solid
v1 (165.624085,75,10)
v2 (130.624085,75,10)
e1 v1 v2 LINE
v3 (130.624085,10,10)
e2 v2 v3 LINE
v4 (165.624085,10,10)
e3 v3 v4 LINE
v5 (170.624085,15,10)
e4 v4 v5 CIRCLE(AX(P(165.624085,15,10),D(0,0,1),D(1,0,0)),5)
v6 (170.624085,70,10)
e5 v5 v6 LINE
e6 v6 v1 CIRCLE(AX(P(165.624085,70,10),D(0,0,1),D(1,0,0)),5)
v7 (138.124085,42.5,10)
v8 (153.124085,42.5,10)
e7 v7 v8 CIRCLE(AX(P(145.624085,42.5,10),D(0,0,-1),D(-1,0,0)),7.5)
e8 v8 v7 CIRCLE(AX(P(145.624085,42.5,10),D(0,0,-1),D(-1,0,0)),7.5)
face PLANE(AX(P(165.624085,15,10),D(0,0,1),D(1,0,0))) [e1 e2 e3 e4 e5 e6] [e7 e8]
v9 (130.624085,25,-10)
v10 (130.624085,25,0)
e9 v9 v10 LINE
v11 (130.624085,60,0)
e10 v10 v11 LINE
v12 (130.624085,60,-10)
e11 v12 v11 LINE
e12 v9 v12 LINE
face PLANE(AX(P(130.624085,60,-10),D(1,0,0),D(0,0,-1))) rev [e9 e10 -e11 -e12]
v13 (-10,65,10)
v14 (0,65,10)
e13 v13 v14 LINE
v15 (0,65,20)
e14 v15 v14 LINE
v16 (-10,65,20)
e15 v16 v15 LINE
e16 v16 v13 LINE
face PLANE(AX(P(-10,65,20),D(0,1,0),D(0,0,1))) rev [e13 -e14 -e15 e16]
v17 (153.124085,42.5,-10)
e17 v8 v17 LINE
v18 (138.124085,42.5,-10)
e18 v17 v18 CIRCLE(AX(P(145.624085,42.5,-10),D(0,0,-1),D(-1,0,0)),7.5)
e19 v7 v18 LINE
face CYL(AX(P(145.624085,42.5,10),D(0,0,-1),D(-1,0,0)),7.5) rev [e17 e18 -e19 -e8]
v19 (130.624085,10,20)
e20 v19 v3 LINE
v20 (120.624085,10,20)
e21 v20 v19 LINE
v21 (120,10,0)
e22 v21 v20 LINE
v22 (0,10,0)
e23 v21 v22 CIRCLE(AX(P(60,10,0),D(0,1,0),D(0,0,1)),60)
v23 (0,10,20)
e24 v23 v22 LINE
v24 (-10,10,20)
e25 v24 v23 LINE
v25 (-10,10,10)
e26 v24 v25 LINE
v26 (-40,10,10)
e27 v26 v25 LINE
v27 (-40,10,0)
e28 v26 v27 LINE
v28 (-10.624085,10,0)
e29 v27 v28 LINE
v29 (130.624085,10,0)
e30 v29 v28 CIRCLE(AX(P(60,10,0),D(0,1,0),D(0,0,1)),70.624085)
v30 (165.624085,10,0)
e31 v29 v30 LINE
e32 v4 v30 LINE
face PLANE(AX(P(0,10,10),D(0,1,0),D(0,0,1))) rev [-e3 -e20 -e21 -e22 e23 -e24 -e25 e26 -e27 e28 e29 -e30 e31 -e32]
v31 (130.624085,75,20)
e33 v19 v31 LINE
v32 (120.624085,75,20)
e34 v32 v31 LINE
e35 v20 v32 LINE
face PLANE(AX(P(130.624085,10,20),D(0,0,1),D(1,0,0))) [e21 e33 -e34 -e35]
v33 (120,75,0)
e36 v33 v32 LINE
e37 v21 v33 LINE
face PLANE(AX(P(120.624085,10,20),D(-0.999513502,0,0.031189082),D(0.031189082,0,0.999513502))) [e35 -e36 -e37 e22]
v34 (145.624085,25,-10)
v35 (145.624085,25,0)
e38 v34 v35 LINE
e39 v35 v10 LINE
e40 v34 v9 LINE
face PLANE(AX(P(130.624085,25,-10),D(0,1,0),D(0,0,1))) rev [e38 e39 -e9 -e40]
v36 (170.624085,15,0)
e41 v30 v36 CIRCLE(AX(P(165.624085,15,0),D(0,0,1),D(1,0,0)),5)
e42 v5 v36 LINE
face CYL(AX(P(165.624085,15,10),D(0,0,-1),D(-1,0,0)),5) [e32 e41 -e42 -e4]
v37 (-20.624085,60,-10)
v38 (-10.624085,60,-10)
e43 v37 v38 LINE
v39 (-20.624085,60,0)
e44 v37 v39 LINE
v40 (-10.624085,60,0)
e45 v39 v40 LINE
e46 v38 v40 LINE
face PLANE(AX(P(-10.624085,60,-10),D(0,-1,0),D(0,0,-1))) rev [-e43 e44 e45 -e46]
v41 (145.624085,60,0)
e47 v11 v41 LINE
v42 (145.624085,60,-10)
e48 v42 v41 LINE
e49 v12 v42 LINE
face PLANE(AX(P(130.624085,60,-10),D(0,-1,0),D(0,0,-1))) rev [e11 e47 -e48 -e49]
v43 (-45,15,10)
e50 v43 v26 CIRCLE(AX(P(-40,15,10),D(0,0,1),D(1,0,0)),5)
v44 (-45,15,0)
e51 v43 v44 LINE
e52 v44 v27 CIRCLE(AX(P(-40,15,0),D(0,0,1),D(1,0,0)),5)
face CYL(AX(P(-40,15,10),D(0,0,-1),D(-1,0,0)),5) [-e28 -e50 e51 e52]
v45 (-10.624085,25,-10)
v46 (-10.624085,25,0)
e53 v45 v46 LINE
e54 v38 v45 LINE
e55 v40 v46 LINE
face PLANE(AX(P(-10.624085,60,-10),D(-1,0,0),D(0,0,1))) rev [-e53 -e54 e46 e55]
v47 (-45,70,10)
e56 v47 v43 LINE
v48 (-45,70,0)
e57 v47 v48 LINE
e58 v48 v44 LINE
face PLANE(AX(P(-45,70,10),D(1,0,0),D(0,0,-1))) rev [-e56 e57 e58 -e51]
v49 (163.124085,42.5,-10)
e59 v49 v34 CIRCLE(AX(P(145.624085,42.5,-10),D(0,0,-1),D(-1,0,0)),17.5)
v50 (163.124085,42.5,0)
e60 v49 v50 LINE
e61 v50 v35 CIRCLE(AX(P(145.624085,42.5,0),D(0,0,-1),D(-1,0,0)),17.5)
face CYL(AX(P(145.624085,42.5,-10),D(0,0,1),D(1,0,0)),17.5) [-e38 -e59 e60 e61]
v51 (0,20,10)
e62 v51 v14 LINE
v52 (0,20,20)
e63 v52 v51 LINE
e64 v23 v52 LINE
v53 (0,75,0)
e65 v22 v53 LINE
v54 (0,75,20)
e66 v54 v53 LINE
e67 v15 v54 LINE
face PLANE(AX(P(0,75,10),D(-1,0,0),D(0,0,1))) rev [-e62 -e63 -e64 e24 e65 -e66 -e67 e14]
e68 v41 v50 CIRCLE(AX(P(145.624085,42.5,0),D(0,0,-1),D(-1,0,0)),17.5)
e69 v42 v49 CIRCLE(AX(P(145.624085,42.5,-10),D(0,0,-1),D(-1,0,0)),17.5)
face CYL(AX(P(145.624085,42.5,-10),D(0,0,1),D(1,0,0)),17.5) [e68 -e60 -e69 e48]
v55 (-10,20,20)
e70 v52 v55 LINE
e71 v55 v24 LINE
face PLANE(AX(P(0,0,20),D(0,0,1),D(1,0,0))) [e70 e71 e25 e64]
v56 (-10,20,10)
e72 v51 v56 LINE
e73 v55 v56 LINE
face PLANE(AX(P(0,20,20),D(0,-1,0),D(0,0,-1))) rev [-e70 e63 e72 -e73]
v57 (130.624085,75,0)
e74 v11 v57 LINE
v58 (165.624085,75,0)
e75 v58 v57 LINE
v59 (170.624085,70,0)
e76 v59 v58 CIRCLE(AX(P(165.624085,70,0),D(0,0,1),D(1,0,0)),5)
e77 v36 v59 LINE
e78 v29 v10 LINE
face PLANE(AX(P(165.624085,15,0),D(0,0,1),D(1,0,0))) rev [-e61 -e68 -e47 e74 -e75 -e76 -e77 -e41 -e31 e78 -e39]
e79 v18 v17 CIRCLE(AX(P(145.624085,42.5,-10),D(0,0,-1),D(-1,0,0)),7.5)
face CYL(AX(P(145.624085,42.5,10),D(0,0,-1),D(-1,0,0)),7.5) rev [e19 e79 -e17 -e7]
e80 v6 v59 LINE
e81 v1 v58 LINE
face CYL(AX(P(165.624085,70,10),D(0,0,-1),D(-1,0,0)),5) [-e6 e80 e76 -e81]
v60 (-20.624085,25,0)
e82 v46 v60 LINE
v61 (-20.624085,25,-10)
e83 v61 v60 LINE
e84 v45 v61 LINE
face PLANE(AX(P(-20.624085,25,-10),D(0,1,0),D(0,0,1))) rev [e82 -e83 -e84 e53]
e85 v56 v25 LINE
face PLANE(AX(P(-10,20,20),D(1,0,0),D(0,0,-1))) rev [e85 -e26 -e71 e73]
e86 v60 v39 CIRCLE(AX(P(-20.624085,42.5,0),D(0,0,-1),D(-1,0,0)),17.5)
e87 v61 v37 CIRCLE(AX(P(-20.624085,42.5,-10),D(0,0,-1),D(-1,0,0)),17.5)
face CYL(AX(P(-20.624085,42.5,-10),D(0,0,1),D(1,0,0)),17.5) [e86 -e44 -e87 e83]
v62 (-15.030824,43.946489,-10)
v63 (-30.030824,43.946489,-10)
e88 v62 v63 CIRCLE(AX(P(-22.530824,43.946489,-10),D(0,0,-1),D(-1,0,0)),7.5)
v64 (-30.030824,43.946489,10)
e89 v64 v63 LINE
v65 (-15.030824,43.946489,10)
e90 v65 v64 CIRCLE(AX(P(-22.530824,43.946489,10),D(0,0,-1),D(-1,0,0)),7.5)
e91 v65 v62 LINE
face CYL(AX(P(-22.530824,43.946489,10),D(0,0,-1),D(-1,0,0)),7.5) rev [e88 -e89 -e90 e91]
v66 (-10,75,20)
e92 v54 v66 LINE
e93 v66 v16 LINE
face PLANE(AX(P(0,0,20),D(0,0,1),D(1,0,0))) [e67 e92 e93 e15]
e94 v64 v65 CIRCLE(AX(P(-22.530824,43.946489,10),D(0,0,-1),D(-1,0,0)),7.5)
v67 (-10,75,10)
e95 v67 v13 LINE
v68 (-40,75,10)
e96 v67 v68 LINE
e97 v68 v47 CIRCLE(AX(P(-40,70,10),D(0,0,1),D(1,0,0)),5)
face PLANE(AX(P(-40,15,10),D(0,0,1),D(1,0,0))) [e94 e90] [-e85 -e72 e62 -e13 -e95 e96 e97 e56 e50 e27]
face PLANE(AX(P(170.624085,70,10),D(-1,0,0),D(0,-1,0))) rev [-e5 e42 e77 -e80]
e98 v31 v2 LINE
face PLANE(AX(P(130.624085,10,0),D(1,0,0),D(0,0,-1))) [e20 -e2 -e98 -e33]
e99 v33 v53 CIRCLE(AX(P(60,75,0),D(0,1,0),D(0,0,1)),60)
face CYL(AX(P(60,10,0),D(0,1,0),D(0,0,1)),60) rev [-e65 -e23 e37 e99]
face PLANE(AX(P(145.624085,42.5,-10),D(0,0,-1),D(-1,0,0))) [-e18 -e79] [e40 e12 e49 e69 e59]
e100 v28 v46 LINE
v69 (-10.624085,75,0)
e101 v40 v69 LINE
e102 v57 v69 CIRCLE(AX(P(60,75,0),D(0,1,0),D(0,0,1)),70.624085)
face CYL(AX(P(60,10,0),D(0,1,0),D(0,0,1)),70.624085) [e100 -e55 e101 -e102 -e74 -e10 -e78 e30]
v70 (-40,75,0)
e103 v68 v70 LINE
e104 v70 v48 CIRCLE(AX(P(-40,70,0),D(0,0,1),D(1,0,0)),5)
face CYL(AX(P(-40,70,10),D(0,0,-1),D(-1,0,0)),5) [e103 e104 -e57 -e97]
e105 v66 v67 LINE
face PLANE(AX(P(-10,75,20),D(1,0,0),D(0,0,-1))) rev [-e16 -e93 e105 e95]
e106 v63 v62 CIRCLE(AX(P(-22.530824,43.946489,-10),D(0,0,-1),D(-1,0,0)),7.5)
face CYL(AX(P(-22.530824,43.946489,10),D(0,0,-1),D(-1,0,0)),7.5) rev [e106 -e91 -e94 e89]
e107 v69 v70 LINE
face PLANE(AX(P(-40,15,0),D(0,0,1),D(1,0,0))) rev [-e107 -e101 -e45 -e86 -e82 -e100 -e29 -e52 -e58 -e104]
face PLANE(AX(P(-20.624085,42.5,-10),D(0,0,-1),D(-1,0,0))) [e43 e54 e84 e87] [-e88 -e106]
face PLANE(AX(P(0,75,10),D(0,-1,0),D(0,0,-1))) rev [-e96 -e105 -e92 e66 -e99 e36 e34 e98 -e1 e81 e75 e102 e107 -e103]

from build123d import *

# Parameters (mm, degrees)
FLANGE_STEP_A_DEPTH  = 10
FLANGE_RIB_SKETCH_W  = 10
FLANGE_RIB_SKETCH_H  = 10
FLANGE_RIB_DEPTH     = 10
CLAMP_BAND_DEPTH     = 65
FLANGE_STEP_B_DEPTH  = 10
FLANGE_WEB_DEPTH     = 65
MOUNTING_LUG_1_DEPTH = 10
MOUNTING_LUG_2_DEPTH = 10
BOLT_HOLE_1_SKETCH_R = 7.5
BOLT_HOLE_1_15_DEPTH = 20
BOLT_HOLE_2_SKETCH_R = 7.5
BOLT_HOLE_2_15_DEPTH = 20


with BuildPart() as part:
    # Flange Step A Sketch → Flange Step A (new body)
    with BuildSketch(Plane.XY):
        with BuildLine():
            Line((0, 10), (-40, 10))
            ThreePointArc((-40, 10), (-43.535533906, 11.464466094), (-45, 15))
            Line((-45, 15), (-45, 70))
            ThreePointArc((-45, 70), (-43.535533906, 73.535533906), (-40, 75))
            Line((-40, 75), (0, 75))
            Line((0, 75), (0, 10))
        make_face()
    extrude(amount=FLANGE_STEP_A_DEPTH)

    # Flange Rib Sketch → Flange Rib (add)
    with BuildSketch(Plane.XY.offset(10)):
        with Locations((-5, 70)):
            Rectangle(FLANGE_RIB_SKETCH_W, FLANGE_RIB_SKETCH_H)
        with Locations((-5, 15)):
            Rectangle(FLANGE_RIB_SKETCH_W, FLANGE_RIB_SKETCH_H)
    extrude(amount=FLANGE_RIB_DEPTH)

    # Clamp Band Sketch → Clamp Band (add)
    with BuildSketch(Plane(origin=(0, 75, 0), x_dir=(1, 0, 0), z_dir=(0, 1, 0))):
        with BuildLine():
            Line((-10.624085248, 0), (0, 0))
            ThreePointArc((0, 0), (60, 60), (120, 0))
            Line((120, 0), (130.624085248, 0))
            ThreePointArc((130.624085248, 0), (60, 70.624085248), (-10.624085248, 0))
        make_face()
    extrude(amount=-CLAMP_BAND_DEPTH)



with BuildPart() as body_2:
    # Flange Step B Sketch → Flange Step B (new body)
    with BuildSketch(Plane.XY):
        with BuildLine():
            Line((130.624085248, 75), (165.624085248, 75))
            ThreePointArc((165.624085248, 75), (169.159619153, 73.535533906), (170.624085248, 70))
            Line((170.624085248, 70), (170.624085248, 15))
            ThreePointArc((170.624085248, 15), (169.159619153, 11.464466094), (165.624085248, 10))
            Line((165.624085248, 10), (130.624085248, 10))
            Line((130.624085248, 10), (130.624085248, 75))
        make_face()
    extrude(amount=FLANGE_STEP_B_DEPTH)


with BuildPart() as part_1:
    add(part.part)

    add(body_2.part)  # Flange Web merges body 2
    # Flange Web Sketch → Flange Web (add)
    with BuildSketch(Plane(origin=(0, 75, 0), x_dir=(1, 0, 0), z_dir=(0, 1, 0))):
        Polygon((130.624085248, 0), (130.624085248, -20), (120.624085248, -20), (120, 0), align=None)
    extrude(amount=-FLANGE_WEB_DEPTH)

    # Mounting Lug 1 Sketch → Mounting Lug 1 (add)
    with BuildSketch(Plane(origin=(0, 0, 0), x_dir=(-1, 0, 0), z_dir=(0, 0, -1))):
        with BuildLine():
            Line((-130.624085248, 60), (-145.624085248, 60))
            ThreePointArc((-145.624085248, 60), (-163.124085248, 42.5), (-145.624085248, 25))
            Line((-145.624085248, 25), (-130.624085248, 25))
            Line((-130.624085248, 25), (-130.624085248, 60))
        make_face()
    extrude(amount=MOUNTING_LUG_1_DEPTH)

    # Mounting Lug 2 Sketch → Mounting Lug 2 (add)
    with BuildSketch(Plane(origin=(0, 0, 0), x_dir=(-1, 0, 0), z_dir=(0, 0, -1))):
        with BuildLine():
            Line((10.624085248, 60), (10.624085248, 25))
            Line((10.624085248, 25), (20.624085248, 25))
            ThreePointArc((20.624085248, 25), (38.124085248, 42.5), (20.624085248, 60))
            Line((20.624085248, 60), (10.624085248, 60))
        make_face()
    extrude(amount=MOUNTING_LUG_2_DEPTH)

    # Bolt Hole 1 Sketch → Bolt Hole 1 Ø15 (cut)
    with BuildSketch(Plane(origin=(0, 0, -10), x_dir=(-1, 0, 0), z_dir=(0, 0, -1))):
        with Locations((-145.624085248, 42.5)):
            Circle(BOLT_HOLE_1_SKETCH_R)
    extrude(amount=-BOLT_HOLE_1_15_DEPTH, mode=Mode.SUBTRACT)

    # Bolt Hole 2 Sketch → Bolt Hole 2 Ø15 (cut)
    with BuildSketch(Plane(origin=(0, 0, -10), x_dir=(-1, 0, 0), z_dir=(0, 0, -1))):
        with Locations((22.530823522, 43.946489257)):
            Circle(BOLT_HOLE_2_SKETCH_R)
    extrude(amount=-BOLT_HOLE_2_15_DEPTH, mode=Mode.SUBTRACT)


solid = part_1.part
